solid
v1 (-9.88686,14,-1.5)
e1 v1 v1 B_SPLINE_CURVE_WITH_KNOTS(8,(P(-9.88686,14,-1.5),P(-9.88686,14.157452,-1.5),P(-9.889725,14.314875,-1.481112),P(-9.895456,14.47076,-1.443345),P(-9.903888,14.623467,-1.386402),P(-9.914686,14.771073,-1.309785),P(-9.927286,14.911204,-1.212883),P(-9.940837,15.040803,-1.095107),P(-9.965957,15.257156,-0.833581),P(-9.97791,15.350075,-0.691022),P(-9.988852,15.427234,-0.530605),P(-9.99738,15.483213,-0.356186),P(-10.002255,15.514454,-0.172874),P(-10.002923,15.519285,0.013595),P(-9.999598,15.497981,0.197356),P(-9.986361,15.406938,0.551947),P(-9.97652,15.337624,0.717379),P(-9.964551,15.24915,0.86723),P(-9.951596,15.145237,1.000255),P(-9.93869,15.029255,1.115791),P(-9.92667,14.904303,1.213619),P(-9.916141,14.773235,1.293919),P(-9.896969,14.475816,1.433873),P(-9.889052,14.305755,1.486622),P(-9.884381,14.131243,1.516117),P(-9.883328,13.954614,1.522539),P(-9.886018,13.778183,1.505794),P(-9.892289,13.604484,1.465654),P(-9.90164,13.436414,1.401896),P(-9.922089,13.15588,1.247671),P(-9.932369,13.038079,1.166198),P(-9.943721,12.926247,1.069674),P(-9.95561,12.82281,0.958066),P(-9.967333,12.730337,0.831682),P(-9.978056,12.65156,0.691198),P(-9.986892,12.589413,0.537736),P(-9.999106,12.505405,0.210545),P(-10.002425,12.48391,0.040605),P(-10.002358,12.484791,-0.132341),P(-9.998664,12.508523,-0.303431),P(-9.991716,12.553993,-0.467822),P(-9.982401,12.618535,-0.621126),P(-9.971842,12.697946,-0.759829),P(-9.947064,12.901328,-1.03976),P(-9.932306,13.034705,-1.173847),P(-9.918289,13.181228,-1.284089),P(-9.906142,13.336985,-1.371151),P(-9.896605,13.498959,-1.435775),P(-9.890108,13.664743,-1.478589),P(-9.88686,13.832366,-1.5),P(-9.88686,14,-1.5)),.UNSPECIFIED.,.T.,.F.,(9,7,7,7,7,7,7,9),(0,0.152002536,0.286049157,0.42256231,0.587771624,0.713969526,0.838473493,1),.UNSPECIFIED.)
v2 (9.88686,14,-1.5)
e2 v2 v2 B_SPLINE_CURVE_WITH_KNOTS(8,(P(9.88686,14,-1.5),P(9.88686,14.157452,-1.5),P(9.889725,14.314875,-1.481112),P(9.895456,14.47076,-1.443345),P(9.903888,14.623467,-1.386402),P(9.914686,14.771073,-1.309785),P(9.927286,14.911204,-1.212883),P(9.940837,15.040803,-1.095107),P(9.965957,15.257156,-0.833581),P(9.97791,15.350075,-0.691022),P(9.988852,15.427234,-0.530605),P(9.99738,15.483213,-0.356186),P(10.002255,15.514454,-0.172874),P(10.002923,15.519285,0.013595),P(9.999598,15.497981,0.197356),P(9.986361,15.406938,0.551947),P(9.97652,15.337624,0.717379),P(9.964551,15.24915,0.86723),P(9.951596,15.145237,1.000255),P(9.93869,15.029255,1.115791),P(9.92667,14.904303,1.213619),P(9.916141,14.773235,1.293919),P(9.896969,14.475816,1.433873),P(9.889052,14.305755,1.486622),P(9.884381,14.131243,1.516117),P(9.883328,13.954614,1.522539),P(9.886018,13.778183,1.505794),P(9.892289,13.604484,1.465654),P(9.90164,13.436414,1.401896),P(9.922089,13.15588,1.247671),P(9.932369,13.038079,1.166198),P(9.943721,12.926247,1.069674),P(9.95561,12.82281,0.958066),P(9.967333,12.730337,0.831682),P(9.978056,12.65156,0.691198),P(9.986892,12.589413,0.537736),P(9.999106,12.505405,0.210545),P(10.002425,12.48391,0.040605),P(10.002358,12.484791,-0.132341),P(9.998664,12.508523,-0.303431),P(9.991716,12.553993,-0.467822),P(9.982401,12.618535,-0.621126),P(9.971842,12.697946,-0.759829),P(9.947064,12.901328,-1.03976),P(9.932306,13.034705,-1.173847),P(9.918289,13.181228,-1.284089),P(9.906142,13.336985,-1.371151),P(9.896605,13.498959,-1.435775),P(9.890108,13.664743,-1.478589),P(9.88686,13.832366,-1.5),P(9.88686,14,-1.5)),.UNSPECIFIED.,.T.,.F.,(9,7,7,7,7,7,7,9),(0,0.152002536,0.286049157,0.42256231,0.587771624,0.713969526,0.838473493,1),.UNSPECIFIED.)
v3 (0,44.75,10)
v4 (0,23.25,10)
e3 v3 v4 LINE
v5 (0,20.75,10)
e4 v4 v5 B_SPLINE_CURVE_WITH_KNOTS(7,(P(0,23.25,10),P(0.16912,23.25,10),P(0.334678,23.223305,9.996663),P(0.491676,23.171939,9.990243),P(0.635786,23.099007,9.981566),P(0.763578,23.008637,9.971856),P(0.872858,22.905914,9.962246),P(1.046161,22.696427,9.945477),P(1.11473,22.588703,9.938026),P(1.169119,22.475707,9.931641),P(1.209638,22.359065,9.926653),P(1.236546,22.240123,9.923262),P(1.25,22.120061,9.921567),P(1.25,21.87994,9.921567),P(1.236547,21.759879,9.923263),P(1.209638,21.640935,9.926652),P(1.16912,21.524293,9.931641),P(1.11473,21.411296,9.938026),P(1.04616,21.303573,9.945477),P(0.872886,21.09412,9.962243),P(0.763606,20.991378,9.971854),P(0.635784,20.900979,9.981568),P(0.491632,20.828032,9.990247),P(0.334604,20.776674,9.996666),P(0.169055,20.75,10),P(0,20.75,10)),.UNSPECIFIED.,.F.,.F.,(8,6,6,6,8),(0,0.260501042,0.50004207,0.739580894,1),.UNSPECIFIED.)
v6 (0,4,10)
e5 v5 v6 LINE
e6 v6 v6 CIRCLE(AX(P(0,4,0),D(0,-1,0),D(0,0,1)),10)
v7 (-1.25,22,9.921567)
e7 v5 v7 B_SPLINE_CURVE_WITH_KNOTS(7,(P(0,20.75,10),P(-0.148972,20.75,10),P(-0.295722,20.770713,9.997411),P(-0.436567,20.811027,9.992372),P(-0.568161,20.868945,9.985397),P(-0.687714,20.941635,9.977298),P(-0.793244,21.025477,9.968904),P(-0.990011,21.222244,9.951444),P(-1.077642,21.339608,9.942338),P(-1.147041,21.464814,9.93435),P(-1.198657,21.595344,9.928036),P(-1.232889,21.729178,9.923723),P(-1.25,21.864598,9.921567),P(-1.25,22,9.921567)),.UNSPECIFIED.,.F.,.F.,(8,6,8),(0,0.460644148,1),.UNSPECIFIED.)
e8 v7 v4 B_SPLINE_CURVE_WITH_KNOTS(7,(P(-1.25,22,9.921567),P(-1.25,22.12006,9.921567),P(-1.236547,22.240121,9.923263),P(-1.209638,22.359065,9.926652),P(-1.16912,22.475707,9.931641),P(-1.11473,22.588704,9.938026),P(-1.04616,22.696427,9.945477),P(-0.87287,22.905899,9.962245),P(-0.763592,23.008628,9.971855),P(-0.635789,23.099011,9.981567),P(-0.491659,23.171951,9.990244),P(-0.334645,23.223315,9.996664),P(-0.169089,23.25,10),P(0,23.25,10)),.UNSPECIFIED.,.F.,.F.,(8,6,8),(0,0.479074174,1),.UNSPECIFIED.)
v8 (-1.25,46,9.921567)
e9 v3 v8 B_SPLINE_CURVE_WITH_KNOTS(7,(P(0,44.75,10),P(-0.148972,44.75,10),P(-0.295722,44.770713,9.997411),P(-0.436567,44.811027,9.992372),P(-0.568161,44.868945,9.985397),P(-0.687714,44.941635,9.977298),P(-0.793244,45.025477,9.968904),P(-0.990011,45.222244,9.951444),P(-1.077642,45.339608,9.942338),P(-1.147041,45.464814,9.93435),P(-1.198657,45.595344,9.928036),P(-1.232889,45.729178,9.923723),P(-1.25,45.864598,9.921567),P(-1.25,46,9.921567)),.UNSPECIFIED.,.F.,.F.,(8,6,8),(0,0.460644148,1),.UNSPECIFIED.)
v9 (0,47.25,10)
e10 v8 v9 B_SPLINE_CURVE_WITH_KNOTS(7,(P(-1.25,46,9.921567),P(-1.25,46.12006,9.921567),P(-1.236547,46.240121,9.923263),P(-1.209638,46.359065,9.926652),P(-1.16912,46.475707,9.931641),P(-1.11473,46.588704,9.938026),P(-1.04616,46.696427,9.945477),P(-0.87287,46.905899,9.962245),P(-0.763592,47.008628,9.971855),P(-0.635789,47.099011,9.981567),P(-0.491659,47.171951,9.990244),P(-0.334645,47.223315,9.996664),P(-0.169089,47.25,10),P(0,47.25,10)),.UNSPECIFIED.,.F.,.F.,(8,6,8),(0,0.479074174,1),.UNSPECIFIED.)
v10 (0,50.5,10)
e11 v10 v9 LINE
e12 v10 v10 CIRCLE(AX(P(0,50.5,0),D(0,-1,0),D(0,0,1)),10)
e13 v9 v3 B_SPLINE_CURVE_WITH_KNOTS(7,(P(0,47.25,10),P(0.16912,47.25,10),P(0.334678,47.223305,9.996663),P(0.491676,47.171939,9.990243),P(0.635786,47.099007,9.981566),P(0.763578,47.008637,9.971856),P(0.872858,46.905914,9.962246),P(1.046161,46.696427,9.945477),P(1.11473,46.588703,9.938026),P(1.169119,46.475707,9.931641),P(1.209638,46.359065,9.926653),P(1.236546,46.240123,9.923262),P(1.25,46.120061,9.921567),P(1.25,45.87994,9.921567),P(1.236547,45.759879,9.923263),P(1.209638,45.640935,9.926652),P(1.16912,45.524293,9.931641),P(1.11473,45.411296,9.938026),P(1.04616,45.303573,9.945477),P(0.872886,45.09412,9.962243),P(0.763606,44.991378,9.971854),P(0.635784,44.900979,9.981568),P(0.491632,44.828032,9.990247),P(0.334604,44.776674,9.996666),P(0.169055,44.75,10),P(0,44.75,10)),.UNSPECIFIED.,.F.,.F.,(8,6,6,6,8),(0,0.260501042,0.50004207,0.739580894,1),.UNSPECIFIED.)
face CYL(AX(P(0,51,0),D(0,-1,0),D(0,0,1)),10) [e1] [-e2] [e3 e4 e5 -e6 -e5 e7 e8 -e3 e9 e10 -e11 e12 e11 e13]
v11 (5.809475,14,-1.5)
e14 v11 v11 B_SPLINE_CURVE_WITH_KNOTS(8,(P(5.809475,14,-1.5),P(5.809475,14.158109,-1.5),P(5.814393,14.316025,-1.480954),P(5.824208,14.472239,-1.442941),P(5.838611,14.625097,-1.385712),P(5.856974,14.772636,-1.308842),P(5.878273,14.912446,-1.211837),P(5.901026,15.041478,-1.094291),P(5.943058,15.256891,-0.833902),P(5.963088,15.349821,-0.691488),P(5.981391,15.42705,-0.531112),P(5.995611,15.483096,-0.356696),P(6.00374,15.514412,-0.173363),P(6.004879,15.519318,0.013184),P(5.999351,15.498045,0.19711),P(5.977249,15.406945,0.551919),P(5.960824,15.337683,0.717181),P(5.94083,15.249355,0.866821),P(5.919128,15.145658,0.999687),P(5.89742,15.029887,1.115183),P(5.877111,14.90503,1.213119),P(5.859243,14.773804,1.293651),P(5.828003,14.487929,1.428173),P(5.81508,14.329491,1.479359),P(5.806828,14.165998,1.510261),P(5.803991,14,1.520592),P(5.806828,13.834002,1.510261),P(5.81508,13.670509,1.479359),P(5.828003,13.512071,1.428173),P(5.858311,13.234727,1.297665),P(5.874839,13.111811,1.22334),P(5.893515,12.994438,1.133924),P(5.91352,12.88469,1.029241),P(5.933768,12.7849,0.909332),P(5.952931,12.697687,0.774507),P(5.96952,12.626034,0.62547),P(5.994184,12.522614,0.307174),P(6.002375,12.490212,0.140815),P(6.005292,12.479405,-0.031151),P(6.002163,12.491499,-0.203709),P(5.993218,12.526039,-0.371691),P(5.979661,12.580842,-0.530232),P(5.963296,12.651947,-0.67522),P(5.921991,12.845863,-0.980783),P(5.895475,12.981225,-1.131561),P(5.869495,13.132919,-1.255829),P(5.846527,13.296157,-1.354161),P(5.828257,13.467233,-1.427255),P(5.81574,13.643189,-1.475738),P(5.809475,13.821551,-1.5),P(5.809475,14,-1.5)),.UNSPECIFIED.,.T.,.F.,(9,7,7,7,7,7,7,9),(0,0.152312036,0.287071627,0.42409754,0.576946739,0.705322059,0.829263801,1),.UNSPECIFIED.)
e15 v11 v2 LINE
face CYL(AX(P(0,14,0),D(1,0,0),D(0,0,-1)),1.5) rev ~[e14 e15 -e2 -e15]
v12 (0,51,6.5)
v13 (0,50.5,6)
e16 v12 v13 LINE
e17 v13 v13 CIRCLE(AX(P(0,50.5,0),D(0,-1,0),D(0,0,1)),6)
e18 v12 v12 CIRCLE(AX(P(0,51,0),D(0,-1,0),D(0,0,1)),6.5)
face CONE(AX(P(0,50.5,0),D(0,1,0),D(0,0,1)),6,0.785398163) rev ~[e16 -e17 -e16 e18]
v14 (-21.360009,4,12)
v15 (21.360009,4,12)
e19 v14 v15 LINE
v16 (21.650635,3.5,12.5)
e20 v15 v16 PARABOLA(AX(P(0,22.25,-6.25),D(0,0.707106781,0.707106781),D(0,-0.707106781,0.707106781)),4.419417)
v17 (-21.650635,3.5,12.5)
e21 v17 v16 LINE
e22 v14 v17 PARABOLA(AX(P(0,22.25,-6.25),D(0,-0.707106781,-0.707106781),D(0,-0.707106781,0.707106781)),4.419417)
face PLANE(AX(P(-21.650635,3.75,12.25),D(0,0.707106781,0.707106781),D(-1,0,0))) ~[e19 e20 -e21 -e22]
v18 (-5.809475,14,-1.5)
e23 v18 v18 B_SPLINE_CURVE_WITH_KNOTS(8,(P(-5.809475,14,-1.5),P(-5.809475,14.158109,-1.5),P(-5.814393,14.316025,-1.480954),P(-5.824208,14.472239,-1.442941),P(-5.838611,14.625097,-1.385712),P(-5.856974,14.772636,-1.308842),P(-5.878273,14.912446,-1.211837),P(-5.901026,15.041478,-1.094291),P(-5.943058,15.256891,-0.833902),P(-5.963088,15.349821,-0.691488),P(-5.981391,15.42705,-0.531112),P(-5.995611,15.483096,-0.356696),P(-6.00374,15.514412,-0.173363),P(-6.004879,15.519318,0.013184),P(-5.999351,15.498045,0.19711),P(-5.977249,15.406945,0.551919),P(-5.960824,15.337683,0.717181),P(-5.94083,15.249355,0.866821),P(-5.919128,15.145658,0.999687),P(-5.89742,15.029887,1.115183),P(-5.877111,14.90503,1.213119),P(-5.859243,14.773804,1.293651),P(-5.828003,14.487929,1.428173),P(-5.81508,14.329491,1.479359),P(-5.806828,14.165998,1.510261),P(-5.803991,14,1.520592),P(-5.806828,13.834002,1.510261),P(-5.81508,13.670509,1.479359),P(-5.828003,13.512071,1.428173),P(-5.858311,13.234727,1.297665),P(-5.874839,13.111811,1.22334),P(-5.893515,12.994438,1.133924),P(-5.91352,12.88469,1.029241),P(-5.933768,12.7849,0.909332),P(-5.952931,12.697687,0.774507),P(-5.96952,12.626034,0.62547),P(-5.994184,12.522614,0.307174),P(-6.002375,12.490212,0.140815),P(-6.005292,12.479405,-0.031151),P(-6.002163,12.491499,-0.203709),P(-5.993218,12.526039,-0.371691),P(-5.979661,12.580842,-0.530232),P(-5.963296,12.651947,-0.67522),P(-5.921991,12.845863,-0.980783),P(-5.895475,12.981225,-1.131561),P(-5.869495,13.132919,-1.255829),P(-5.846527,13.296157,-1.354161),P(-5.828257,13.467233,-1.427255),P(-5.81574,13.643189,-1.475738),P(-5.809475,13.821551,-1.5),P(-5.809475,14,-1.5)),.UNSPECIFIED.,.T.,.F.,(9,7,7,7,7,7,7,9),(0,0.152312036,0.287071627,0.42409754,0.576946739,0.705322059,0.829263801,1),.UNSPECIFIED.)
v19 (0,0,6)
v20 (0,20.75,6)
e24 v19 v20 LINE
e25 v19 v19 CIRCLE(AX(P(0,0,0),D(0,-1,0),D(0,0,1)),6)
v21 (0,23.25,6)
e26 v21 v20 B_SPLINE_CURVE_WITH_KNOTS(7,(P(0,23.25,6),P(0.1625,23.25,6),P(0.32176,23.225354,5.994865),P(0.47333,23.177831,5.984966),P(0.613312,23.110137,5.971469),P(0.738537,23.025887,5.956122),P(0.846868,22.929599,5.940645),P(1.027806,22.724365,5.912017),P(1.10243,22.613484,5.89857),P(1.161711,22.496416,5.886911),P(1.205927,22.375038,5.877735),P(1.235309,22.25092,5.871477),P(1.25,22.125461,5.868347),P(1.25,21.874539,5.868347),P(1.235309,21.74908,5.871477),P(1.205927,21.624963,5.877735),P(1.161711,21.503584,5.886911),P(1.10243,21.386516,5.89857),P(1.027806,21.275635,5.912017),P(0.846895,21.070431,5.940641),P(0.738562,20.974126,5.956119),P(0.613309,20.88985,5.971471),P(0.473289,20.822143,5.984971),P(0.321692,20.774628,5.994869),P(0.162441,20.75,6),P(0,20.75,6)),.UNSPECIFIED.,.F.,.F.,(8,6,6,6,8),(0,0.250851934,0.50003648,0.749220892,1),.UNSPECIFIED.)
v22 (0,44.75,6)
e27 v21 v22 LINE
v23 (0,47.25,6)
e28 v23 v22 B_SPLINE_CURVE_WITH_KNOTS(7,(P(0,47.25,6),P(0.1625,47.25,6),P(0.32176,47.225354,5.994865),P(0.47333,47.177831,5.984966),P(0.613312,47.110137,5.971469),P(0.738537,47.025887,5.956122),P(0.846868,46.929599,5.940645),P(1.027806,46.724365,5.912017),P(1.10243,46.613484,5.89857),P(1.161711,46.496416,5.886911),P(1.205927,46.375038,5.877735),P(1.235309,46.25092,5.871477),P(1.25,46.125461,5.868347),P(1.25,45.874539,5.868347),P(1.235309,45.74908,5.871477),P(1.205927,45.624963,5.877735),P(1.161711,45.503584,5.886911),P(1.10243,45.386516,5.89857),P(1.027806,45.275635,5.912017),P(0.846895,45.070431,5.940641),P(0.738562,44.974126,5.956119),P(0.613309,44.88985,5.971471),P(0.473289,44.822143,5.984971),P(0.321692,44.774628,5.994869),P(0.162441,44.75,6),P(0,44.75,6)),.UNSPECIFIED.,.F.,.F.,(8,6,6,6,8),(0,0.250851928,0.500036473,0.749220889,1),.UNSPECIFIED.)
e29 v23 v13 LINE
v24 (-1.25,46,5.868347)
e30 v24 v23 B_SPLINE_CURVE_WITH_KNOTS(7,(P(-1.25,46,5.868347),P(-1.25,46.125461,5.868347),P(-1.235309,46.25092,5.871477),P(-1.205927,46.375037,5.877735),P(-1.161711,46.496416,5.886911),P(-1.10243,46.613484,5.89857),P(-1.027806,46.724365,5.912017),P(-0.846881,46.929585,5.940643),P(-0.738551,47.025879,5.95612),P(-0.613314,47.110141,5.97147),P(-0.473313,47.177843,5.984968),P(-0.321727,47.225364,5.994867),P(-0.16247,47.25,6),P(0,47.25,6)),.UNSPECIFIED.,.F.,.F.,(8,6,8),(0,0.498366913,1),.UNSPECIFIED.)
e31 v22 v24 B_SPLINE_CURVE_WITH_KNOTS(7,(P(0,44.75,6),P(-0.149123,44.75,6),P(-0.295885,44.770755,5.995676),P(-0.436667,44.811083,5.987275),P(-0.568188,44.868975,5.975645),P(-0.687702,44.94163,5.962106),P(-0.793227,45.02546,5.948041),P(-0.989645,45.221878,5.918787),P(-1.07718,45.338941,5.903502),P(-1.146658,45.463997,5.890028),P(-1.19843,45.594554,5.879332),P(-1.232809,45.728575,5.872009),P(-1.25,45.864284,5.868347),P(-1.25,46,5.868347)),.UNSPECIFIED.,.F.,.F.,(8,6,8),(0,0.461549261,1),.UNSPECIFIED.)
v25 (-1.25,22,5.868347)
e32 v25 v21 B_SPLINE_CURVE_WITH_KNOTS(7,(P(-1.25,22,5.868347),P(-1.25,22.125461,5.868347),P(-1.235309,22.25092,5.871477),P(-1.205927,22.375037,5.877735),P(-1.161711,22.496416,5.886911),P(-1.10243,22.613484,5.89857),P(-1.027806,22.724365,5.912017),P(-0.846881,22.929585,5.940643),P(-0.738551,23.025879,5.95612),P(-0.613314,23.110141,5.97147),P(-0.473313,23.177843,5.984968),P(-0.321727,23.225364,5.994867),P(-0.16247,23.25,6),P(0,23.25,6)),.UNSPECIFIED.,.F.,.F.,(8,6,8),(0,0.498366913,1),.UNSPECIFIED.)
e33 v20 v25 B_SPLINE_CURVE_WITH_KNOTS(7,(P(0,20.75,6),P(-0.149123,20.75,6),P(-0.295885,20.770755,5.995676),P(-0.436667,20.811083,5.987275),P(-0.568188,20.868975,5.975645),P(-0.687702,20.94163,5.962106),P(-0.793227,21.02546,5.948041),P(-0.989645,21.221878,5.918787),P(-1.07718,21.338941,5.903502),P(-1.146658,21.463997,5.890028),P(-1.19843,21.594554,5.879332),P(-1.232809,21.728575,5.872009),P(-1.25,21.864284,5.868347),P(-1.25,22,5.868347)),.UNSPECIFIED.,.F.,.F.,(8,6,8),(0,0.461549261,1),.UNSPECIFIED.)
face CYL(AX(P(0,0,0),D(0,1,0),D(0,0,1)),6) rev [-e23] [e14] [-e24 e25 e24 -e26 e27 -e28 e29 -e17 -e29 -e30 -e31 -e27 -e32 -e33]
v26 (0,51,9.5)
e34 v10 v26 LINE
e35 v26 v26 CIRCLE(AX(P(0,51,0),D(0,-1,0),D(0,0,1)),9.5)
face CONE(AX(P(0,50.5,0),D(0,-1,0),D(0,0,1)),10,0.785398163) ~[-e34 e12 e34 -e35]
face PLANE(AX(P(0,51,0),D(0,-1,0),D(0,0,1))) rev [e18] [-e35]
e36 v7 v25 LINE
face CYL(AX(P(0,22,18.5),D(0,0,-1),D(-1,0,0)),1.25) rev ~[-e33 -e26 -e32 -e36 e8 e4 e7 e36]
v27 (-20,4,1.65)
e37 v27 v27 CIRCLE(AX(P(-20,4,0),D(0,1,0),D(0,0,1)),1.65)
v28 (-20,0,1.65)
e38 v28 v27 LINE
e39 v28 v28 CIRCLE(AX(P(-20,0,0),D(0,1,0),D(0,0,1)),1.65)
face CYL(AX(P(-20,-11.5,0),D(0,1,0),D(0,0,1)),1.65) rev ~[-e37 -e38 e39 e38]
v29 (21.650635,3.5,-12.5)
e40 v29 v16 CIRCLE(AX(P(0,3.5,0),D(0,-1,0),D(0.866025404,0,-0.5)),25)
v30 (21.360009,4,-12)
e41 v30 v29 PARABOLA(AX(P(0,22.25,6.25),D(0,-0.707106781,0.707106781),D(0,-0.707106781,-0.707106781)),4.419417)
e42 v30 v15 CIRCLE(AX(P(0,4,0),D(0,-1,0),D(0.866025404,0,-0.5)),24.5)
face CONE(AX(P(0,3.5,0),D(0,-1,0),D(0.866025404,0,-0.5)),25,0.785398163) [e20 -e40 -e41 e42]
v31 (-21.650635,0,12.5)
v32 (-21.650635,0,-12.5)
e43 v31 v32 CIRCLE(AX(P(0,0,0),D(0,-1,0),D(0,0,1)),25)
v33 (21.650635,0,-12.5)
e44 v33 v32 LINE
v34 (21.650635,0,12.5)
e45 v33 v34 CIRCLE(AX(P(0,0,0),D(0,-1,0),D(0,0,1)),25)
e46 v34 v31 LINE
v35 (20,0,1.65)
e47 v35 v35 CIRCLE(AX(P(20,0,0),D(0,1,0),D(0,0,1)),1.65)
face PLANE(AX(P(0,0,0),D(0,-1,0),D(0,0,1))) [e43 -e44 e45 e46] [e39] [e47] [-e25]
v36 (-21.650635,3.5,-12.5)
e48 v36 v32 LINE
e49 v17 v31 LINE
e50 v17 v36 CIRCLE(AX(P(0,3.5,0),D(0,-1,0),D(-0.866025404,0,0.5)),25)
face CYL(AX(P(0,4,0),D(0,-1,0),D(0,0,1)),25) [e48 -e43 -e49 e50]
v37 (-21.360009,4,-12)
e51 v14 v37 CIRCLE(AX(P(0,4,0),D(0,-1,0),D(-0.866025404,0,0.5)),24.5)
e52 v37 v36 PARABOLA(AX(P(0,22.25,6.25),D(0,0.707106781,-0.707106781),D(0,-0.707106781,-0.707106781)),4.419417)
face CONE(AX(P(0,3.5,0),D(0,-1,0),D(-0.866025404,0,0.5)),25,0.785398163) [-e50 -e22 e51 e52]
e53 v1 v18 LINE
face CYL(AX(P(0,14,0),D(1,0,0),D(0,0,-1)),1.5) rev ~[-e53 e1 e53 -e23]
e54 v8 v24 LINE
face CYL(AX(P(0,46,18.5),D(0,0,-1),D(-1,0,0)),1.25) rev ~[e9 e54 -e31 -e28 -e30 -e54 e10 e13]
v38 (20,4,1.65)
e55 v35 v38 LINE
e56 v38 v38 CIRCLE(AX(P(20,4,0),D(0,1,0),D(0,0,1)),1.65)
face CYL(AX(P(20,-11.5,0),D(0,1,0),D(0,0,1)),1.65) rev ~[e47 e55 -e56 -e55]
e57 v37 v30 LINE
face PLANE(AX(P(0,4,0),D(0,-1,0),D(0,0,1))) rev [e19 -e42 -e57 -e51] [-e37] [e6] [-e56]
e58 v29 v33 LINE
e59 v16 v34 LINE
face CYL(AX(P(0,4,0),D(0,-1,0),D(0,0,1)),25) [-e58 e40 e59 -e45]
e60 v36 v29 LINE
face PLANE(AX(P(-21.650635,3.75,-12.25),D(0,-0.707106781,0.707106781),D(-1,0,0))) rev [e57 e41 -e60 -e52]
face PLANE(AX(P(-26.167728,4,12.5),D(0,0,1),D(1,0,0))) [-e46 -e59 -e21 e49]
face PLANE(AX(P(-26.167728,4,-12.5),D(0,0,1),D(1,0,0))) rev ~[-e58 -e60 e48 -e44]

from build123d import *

# Parameters (mm, degrees)
CUT_EXTRUDE3_DEPTH    = 10
CHAMFER2_SIZE         = 0.5
M3_TAPPED_HOLE1_D     = 2.5
M3_TAPPED_HOLE1_DEPTH = 8.5
M3_TAPPED_HOLE1_TIP   = 0.751075774
M4_TAPPED_HOLE1_D     = 3.3
M4_TAPPED_HOLE1_DEPTH = 11.5
M4_TAPPED_HOLE1_TIP   = 0.991420021
SKETCH16_R            = 1.5
CUT_EXTRUDE4_DEPTH    = 26.5


with BuildPart() as part:
    # Sketch1 → Revolve1 (revolve)
    with BuildSketch(Plane.XY, mode=Mode.PRIVATE) as revolve1_sk:
        Polygon((10, 51), (10, 4), (25, 4), (25, 0), (6, 0), (6, 51), align=None)
    revolve(revolve1_sk.sketch.rotate(Axis((0, 57.582524272, 0), (0, -1, 0)), 90), axis=Axis((0, 57.582524272, 0), (0, -1, 0)))

    # Sketch9 → Cut-Extrude3 (cut)
    with BuildSketch(Plane(origin=(0, 4, 0), x_dir=(1, 0, 0), z_dir=(0, 1, 0))):
        with BuildLine():
            Line((-26.167728216, -12.5), (26.167728216, -12.5))
            ThreePointArc((26.167728216, -12.5), (0, -29), (-26.167728216, -12.5))
        make_face()
        with BuildLine():
            Line((-26.167728216, 12.5), (26.167728216, 12.5))
            ThreePointArc((26.167728216, 12.5), (0, 29), (-26.167728216, 12.5))
        make_face()
    extrude(amount=-CUT_EXTRUDE3_DEPTH, mode=Mode.SUBTRACT)

    # Chamfer2
    chamfer2_edges = [part.edges().sort_by_distance(p)[0] for p in [
        (-25, 4, 0),
        (0, 4, -12.5),
        (25, 4, 0),
        (0, 4, 12.5),
        (0, 51, -6),
        (0, 51, -10),
    ]]
    chamfer(chamfer2_edges, length=CHAMFER2_SIZE)

    # M3 Tapped Hole1
    with Locations(Plane(origin=(0, 22, 10), x_dir=(1, 0, 0), z_dir=(0, 0, 1))):
        with Locations((0, 0), (0, 24)):
            Hole(M3_TAPPED_HOLE1_D / 2, depth=M3_TAPPED_HOLE1_DEPTH)
            with Locations((0, 0, -(M3_TAPPED_HOLE1_DEPTH + M3_TAPPED_HOLE1_TIP / 2))):  # 118° drill point
                Cone(0, M3_TAPPED_HOLE1_D / 2, M3_TAPPED_HOLE1_TIP, mode=Mode.SUBTRACT)

    # M4 Tapped Hole1
    with Locations(Plane(origin=(-20, 0, 0), x_dir=(0, 0, -1), z_dir=(0, -1, 0))):
        with Locations((0, 0), (0, 40)):
            Hole(M4_TAPPED_HOLE1_D / 2, depth=M4_TAPPED_HOLE1_DEPTH)
            with Locations((0, 0, -(M4_TAPPED_HOLE1_DEPTH + M4_TAPPED_HOLE1_TIP / 2))):  # 118° drill point
                Cone(0, M4_TAPPED_HOLE1_D / 2, M4_TAPPED_HOLE1_TIP, mode=Mode.SUBTRACT)

    # Sketch16 → Cut-Extrude4 (cut, symmetric)
    with BuildSketch(Plane(origin=(0, 0, 0), x_dir=(0, 0, -1), z_dir=(1, 0, 0))):
        with Locations((0, 14)):
            Circle(SKETCH16_R)
    extrude(amount=CUT_EXTRUDE4_DEPTH, both=True, mode=Mode.SUBTRACT)


solid = part.part
